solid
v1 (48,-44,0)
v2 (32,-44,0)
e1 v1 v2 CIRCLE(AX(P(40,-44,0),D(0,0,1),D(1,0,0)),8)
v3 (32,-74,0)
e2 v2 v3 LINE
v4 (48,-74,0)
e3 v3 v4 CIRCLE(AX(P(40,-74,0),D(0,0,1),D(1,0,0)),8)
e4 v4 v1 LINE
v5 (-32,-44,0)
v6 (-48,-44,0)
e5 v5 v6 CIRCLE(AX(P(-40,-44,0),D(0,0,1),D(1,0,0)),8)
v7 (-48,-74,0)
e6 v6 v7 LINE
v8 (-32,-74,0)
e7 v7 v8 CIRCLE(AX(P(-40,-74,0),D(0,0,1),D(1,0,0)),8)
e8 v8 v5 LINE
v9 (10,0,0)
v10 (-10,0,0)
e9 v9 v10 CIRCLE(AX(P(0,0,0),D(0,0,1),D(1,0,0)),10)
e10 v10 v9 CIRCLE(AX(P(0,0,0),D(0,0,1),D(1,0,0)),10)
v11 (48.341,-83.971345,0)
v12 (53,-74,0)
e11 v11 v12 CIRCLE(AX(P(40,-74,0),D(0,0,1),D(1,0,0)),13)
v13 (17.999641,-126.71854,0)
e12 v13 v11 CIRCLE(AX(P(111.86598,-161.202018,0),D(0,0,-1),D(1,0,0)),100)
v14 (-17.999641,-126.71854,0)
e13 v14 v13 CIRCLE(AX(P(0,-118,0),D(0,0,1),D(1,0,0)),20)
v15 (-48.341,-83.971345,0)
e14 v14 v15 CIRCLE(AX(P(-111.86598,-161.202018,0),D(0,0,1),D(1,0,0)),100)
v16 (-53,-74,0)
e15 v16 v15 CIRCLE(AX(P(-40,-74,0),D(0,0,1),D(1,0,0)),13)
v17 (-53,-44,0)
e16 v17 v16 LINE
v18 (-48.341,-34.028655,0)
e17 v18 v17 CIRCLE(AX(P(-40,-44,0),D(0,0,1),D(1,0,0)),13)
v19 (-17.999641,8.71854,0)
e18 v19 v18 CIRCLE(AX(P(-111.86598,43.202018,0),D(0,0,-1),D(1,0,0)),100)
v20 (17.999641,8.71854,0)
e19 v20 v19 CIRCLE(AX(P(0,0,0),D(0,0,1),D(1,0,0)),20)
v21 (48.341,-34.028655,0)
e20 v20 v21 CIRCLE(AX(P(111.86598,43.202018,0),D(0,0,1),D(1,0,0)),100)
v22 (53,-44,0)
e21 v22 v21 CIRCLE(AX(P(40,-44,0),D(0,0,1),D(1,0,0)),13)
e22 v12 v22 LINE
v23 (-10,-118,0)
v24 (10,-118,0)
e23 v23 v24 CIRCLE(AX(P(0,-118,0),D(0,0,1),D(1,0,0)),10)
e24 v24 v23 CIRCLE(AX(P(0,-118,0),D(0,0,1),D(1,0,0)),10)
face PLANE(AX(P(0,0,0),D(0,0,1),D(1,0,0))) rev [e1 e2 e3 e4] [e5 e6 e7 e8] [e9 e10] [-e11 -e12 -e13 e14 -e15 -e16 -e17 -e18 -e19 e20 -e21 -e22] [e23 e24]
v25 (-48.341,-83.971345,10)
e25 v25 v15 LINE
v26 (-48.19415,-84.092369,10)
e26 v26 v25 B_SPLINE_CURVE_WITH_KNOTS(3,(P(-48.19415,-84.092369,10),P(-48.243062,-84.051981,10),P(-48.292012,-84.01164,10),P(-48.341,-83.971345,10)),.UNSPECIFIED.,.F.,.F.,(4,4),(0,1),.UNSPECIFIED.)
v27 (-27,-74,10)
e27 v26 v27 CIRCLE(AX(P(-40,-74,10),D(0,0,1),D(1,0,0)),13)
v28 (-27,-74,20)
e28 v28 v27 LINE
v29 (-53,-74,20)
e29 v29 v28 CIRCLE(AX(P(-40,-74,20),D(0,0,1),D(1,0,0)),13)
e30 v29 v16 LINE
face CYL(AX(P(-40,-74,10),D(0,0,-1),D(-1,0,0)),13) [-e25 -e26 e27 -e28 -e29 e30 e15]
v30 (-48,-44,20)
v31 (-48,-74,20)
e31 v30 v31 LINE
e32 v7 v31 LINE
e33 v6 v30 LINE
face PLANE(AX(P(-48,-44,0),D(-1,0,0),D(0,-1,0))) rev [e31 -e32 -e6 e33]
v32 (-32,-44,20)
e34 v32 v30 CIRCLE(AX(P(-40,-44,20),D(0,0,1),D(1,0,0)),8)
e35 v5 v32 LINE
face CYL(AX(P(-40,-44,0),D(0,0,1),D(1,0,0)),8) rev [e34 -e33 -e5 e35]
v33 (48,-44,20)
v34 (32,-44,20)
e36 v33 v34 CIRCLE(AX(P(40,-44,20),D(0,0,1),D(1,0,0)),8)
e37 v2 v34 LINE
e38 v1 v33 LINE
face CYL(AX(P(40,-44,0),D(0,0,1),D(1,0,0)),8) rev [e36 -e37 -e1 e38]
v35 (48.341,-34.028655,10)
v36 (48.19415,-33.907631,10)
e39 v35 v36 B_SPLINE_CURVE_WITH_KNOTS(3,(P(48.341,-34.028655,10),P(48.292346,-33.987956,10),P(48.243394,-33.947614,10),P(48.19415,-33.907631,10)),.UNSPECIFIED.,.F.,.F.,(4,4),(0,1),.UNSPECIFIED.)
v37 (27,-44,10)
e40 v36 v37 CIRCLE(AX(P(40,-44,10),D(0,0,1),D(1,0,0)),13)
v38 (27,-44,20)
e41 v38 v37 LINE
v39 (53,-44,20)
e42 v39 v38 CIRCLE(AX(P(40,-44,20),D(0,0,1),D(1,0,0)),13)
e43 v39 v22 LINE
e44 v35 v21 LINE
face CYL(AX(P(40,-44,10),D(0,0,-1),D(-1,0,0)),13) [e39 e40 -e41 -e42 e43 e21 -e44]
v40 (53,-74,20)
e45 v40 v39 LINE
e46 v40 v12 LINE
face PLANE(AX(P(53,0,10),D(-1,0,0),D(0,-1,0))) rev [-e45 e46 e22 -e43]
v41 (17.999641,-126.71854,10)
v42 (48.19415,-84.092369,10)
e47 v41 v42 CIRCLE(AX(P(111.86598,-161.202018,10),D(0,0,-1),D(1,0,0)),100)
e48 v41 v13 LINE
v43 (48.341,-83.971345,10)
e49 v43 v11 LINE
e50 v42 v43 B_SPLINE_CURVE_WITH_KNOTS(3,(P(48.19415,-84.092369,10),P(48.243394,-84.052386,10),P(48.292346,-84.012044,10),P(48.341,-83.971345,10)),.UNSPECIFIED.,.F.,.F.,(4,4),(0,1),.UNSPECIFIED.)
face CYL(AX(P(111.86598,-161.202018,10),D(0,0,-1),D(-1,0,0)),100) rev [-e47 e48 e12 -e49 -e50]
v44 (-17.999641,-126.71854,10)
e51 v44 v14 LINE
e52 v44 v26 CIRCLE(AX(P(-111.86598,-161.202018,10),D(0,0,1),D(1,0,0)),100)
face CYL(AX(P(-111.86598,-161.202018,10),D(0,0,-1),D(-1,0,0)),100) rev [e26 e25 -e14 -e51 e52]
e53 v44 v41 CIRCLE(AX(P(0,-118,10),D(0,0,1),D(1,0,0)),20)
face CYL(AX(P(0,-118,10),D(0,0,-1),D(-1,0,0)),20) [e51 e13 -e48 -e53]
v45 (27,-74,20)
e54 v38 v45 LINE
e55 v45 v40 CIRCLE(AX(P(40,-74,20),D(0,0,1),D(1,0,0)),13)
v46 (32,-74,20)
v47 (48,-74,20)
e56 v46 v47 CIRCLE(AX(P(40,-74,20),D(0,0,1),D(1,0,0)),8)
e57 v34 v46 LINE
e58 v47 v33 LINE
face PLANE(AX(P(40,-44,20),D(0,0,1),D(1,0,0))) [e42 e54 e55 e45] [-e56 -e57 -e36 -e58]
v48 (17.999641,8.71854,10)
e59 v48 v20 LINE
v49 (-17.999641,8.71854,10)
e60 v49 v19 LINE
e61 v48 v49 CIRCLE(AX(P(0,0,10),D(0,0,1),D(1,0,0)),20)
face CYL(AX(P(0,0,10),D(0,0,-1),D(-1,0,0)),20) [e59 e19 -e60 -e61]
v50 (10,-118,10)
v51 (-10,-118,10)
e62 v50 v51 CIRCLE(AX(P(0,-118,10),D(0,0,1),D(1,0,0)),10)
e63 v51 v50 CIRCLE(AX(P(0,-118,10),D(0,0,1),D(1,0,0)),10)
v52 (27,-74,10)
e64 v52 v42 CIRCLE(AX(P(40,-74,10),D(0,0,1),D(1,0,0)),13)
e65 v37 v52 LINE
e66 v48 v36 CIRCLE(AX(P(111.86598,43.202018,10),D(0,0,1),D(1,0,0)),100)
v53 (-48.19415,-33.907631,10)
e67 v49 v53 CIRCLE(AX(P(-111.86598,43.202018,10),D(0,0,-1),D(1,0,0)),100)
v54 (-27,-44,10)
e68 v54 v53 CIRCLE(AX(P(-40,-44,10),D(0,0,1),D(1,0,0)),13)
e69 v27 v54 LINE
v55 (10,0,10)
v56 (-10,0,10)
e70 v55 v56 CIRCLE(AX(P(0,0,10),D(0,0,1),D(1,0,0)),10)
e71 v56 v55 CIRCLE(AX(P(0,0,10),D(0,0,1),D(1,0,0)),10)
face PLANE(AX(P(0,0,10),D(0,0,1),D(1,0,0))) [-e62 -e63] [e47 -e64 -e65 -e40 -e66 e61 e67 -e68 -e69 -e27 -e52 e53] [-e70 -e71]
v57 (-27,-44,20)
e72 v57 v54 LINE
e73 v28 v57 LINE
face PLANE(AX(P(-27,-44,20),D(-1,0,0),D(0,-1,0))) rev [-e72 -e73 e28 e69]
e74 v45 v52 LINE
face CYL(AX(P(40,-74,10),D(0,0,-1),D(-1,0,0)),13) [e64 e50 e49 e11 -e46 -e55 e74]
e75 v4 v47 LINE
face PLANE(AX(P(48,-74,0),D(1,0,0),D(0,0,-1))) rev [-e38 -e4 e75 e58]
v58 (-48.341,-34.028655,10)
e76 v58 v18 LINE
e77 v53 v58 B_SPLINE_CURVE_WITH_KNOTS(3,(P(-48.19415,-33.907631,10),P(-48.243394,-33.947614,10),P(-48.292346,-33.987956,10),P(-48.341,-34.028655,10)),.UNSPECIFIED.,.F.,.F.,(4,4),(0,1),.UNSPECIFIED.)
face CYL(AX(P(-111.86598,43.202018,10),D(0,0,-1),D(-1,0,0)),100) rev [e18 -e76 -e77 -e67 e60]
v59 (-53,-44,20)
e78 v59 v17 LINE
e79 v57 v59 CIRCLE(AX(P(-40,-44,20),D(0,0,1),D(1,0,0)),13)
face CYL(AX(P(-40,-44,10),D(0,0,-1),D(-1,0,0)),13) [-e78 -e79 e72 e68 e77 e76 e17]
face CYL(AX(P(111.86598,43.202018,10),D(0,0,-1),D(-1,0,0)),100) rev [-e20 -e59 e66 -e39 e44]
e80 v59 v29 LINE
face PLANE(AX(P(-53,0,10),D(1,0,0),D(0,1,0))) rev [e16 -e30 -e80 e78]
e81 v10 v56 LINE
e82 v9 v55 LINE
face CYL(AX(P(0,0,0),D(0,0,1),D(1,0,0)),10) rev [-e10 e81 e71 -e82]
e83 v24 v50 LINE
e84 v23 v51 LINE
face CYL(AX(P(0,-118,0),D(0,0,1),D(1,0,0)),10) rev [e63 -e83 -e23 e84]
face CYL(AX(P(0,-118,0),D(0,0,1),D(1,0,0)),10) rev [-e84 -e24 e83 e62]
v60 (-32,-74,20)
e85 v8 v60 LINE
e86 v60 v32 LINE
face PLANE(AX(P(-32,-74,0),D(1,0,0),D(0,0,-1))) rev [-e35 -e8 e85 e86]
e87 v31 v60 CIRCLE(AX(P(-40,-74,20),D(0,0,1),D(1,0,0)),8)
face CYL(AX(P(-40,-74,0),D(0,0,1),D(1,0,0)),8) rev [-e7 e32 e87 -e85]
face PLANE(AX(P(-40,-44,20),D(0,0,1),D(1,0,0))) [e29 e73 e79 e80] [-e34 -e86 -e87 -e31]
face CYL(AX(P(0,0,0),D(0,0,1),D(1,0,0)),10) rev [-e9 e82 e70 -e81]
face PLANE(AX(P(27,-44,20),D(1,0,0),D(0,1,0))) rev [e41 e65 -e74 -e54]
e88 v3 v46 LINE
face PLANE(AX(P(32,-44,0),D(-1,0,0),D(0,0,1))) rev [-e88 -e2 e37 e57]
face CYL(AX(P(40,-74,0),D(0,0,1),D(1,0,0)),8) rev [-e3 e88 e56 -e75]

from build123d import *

# Parameters (mm, degrees)
DIAMOND_PLATE_DEPTH    = 10
THROUGH_SLOTS_2X_DEPTH = 10
SLOT_BOSS_A_DEPTH      = 10
END_HOLES_PROFILE_R    = 10
END_HOLES_2X_DEPTH     = 10
SLOT_BOSS_B_DEPTH      = 10


with BuildPart() as part:
    # Diamond Plate Profile → Diamond Plate (new body)
    with BuildSketch(Plane.XY):
        with BuildLine():
            ThreePointArc((48.341000131, -83.971344784), (51.777796944, -79.503044534), (53, -74))
            Line((53, -74), (53, -44))
            ThreePointArc((53, -44), (51.777796944, -38.496955466), (48.341000131, -34.028655216))
            ThreePointArc((48.341000131, -34.028655216), (30.319444036, -14.678569552), (17.999640508, 8.718540106))
            ThreePointArc((17.999640508, 8.718540106), (0, 20), (-17.999640508, 8.718540106))
            ThreePointArc((-17.999640508, 8.718540106), (-30.319444036, -14.678569552), (-48.341000131, -34.028655216))
            ThreePointArc((-48.341000131, -34.028655216), (-51.777796944, -38.496955466), (-53, -44))
            Line((-53, -44), (-53, -74))
            ThreePointArc((-53, -74), (-51.777796944, -79.503044534), (-48.341000131, -83.971344784))
            ThreePointArc((-48.341000131, -83.971344784), (-48.2675462, -84.031821869), (-48.194149845, -84.092368816))
            ThreePointArc((-48.194149845, -84.092368816), (-30.264409293, -103.399045748), (-17.999640508, -126.718540106))
            ThreePointArc((-17.999640508, -126.718540106), (0, -138), (17.999640508, -126.718540106))
            ThreePointArc((17.999640508, -126.718540106), (30.319444036, -103.321430448), (48.341000131, -83.971344784))
        make_face()
    extrude(amount=DIAMOND_PLATE_DEPTH)

    # Slot Cuts Profile → Through Slots 2x (cut)
    with BuildSketch(Plane.XY.offset(10)):
        with BuildLine():
            Line((-47.999999999, -44), (-47.999999999, -74))
            ThreePointArc((-47.999999999, -74), (-40, -81.999999999), (-32, -74))
            Line((-32, -74), (-32, -44))
            ThreePointArc((-32, -44), (-40, -36.000000001), (-47.999999999, -44))
        make_face()
        with BuildLine():
            Line((32, -44), (32, -74))
            ThreePointArc((32, -74), (40, -81.999999999), (47.999999999, -74))
            Line((47.999999999, -74), (47.999999999, -44))
            ThreePointArc((47.999999999, -44), (40, -36.000000001), (32, -44))
        make_face()
    extrude(amount=-THROUGH_SLOTS_2X_DEPTH, mode=Mode.SUBTRACT)

    # Slot Boss A Profile → Slot Boss A (add)
    with BuildSketch(Plane.XY.offset(10)):
        with BuildLine():
            Line((-27, -44), (-27, -74))
            ThreePointArc((-27, -74), (-40, -87), (-53, -74))
            Line((-53, -74), (-53, -44))
            ThreePointArc((-53, -44), (-40, -31), (-27, -44))
        make_face()
        with BuildLine():
            Line((-32, -44), (-32, -74))
            ThreePointArc((-32, -74), (-40, -81.999999999), (-47.999999999, -74))
            Line((-47.999999999, -74), (-47.999999999, -44))
            ThreePointArc((-47.999999999, -44), (-40, -36.000000001), (-32, -44))
        make_face(mode=Mode.SUBTRACT)
    extrude(amount=SLOT_BOSS_A_DEPTH)

    # End Holes Profile → End Holes 2x (cut)
    with BuildSketch(Plane.XY.offset(10)):
        Circle(END_HOLES_PROFILE_R)
        with Locations((0, -118)):
            Circle(END_HOLES_PROFILE_R)
    extrude(amount=-END_HOLES_2X_DEPTH, mode=Mode.SUBTRACT)

    # Slot Boss B Profile → Slot Boss B (add)
    with BuildSketch(Plane.XY.offset(10)):
        with BuildLine():
            Line((27, -44), (27, -74))
            ThreePointArc((27, -74), (40, -87), (53, -74))
            Line((53, -74), (53, -44))
            ThreePointArc((53, -44), (40, -31), (27, -44))
        make_face()
        with BuildLine():
            Line((32, -44), (32, -74))
            ThreePointArc((32, -74), (40, -81.999999999), (47.999999999, -74))
            Line((47.999999999, -74), (47.999999999, -44))
            ThreePointArc((47.999999999, -44), (40, -36.000000001), (32, -44))
        make_face(mode=Mode.SUBTRACT)
    extrude(amount=SLOT_BOSS_B_DEPTH)


solid = part.part
